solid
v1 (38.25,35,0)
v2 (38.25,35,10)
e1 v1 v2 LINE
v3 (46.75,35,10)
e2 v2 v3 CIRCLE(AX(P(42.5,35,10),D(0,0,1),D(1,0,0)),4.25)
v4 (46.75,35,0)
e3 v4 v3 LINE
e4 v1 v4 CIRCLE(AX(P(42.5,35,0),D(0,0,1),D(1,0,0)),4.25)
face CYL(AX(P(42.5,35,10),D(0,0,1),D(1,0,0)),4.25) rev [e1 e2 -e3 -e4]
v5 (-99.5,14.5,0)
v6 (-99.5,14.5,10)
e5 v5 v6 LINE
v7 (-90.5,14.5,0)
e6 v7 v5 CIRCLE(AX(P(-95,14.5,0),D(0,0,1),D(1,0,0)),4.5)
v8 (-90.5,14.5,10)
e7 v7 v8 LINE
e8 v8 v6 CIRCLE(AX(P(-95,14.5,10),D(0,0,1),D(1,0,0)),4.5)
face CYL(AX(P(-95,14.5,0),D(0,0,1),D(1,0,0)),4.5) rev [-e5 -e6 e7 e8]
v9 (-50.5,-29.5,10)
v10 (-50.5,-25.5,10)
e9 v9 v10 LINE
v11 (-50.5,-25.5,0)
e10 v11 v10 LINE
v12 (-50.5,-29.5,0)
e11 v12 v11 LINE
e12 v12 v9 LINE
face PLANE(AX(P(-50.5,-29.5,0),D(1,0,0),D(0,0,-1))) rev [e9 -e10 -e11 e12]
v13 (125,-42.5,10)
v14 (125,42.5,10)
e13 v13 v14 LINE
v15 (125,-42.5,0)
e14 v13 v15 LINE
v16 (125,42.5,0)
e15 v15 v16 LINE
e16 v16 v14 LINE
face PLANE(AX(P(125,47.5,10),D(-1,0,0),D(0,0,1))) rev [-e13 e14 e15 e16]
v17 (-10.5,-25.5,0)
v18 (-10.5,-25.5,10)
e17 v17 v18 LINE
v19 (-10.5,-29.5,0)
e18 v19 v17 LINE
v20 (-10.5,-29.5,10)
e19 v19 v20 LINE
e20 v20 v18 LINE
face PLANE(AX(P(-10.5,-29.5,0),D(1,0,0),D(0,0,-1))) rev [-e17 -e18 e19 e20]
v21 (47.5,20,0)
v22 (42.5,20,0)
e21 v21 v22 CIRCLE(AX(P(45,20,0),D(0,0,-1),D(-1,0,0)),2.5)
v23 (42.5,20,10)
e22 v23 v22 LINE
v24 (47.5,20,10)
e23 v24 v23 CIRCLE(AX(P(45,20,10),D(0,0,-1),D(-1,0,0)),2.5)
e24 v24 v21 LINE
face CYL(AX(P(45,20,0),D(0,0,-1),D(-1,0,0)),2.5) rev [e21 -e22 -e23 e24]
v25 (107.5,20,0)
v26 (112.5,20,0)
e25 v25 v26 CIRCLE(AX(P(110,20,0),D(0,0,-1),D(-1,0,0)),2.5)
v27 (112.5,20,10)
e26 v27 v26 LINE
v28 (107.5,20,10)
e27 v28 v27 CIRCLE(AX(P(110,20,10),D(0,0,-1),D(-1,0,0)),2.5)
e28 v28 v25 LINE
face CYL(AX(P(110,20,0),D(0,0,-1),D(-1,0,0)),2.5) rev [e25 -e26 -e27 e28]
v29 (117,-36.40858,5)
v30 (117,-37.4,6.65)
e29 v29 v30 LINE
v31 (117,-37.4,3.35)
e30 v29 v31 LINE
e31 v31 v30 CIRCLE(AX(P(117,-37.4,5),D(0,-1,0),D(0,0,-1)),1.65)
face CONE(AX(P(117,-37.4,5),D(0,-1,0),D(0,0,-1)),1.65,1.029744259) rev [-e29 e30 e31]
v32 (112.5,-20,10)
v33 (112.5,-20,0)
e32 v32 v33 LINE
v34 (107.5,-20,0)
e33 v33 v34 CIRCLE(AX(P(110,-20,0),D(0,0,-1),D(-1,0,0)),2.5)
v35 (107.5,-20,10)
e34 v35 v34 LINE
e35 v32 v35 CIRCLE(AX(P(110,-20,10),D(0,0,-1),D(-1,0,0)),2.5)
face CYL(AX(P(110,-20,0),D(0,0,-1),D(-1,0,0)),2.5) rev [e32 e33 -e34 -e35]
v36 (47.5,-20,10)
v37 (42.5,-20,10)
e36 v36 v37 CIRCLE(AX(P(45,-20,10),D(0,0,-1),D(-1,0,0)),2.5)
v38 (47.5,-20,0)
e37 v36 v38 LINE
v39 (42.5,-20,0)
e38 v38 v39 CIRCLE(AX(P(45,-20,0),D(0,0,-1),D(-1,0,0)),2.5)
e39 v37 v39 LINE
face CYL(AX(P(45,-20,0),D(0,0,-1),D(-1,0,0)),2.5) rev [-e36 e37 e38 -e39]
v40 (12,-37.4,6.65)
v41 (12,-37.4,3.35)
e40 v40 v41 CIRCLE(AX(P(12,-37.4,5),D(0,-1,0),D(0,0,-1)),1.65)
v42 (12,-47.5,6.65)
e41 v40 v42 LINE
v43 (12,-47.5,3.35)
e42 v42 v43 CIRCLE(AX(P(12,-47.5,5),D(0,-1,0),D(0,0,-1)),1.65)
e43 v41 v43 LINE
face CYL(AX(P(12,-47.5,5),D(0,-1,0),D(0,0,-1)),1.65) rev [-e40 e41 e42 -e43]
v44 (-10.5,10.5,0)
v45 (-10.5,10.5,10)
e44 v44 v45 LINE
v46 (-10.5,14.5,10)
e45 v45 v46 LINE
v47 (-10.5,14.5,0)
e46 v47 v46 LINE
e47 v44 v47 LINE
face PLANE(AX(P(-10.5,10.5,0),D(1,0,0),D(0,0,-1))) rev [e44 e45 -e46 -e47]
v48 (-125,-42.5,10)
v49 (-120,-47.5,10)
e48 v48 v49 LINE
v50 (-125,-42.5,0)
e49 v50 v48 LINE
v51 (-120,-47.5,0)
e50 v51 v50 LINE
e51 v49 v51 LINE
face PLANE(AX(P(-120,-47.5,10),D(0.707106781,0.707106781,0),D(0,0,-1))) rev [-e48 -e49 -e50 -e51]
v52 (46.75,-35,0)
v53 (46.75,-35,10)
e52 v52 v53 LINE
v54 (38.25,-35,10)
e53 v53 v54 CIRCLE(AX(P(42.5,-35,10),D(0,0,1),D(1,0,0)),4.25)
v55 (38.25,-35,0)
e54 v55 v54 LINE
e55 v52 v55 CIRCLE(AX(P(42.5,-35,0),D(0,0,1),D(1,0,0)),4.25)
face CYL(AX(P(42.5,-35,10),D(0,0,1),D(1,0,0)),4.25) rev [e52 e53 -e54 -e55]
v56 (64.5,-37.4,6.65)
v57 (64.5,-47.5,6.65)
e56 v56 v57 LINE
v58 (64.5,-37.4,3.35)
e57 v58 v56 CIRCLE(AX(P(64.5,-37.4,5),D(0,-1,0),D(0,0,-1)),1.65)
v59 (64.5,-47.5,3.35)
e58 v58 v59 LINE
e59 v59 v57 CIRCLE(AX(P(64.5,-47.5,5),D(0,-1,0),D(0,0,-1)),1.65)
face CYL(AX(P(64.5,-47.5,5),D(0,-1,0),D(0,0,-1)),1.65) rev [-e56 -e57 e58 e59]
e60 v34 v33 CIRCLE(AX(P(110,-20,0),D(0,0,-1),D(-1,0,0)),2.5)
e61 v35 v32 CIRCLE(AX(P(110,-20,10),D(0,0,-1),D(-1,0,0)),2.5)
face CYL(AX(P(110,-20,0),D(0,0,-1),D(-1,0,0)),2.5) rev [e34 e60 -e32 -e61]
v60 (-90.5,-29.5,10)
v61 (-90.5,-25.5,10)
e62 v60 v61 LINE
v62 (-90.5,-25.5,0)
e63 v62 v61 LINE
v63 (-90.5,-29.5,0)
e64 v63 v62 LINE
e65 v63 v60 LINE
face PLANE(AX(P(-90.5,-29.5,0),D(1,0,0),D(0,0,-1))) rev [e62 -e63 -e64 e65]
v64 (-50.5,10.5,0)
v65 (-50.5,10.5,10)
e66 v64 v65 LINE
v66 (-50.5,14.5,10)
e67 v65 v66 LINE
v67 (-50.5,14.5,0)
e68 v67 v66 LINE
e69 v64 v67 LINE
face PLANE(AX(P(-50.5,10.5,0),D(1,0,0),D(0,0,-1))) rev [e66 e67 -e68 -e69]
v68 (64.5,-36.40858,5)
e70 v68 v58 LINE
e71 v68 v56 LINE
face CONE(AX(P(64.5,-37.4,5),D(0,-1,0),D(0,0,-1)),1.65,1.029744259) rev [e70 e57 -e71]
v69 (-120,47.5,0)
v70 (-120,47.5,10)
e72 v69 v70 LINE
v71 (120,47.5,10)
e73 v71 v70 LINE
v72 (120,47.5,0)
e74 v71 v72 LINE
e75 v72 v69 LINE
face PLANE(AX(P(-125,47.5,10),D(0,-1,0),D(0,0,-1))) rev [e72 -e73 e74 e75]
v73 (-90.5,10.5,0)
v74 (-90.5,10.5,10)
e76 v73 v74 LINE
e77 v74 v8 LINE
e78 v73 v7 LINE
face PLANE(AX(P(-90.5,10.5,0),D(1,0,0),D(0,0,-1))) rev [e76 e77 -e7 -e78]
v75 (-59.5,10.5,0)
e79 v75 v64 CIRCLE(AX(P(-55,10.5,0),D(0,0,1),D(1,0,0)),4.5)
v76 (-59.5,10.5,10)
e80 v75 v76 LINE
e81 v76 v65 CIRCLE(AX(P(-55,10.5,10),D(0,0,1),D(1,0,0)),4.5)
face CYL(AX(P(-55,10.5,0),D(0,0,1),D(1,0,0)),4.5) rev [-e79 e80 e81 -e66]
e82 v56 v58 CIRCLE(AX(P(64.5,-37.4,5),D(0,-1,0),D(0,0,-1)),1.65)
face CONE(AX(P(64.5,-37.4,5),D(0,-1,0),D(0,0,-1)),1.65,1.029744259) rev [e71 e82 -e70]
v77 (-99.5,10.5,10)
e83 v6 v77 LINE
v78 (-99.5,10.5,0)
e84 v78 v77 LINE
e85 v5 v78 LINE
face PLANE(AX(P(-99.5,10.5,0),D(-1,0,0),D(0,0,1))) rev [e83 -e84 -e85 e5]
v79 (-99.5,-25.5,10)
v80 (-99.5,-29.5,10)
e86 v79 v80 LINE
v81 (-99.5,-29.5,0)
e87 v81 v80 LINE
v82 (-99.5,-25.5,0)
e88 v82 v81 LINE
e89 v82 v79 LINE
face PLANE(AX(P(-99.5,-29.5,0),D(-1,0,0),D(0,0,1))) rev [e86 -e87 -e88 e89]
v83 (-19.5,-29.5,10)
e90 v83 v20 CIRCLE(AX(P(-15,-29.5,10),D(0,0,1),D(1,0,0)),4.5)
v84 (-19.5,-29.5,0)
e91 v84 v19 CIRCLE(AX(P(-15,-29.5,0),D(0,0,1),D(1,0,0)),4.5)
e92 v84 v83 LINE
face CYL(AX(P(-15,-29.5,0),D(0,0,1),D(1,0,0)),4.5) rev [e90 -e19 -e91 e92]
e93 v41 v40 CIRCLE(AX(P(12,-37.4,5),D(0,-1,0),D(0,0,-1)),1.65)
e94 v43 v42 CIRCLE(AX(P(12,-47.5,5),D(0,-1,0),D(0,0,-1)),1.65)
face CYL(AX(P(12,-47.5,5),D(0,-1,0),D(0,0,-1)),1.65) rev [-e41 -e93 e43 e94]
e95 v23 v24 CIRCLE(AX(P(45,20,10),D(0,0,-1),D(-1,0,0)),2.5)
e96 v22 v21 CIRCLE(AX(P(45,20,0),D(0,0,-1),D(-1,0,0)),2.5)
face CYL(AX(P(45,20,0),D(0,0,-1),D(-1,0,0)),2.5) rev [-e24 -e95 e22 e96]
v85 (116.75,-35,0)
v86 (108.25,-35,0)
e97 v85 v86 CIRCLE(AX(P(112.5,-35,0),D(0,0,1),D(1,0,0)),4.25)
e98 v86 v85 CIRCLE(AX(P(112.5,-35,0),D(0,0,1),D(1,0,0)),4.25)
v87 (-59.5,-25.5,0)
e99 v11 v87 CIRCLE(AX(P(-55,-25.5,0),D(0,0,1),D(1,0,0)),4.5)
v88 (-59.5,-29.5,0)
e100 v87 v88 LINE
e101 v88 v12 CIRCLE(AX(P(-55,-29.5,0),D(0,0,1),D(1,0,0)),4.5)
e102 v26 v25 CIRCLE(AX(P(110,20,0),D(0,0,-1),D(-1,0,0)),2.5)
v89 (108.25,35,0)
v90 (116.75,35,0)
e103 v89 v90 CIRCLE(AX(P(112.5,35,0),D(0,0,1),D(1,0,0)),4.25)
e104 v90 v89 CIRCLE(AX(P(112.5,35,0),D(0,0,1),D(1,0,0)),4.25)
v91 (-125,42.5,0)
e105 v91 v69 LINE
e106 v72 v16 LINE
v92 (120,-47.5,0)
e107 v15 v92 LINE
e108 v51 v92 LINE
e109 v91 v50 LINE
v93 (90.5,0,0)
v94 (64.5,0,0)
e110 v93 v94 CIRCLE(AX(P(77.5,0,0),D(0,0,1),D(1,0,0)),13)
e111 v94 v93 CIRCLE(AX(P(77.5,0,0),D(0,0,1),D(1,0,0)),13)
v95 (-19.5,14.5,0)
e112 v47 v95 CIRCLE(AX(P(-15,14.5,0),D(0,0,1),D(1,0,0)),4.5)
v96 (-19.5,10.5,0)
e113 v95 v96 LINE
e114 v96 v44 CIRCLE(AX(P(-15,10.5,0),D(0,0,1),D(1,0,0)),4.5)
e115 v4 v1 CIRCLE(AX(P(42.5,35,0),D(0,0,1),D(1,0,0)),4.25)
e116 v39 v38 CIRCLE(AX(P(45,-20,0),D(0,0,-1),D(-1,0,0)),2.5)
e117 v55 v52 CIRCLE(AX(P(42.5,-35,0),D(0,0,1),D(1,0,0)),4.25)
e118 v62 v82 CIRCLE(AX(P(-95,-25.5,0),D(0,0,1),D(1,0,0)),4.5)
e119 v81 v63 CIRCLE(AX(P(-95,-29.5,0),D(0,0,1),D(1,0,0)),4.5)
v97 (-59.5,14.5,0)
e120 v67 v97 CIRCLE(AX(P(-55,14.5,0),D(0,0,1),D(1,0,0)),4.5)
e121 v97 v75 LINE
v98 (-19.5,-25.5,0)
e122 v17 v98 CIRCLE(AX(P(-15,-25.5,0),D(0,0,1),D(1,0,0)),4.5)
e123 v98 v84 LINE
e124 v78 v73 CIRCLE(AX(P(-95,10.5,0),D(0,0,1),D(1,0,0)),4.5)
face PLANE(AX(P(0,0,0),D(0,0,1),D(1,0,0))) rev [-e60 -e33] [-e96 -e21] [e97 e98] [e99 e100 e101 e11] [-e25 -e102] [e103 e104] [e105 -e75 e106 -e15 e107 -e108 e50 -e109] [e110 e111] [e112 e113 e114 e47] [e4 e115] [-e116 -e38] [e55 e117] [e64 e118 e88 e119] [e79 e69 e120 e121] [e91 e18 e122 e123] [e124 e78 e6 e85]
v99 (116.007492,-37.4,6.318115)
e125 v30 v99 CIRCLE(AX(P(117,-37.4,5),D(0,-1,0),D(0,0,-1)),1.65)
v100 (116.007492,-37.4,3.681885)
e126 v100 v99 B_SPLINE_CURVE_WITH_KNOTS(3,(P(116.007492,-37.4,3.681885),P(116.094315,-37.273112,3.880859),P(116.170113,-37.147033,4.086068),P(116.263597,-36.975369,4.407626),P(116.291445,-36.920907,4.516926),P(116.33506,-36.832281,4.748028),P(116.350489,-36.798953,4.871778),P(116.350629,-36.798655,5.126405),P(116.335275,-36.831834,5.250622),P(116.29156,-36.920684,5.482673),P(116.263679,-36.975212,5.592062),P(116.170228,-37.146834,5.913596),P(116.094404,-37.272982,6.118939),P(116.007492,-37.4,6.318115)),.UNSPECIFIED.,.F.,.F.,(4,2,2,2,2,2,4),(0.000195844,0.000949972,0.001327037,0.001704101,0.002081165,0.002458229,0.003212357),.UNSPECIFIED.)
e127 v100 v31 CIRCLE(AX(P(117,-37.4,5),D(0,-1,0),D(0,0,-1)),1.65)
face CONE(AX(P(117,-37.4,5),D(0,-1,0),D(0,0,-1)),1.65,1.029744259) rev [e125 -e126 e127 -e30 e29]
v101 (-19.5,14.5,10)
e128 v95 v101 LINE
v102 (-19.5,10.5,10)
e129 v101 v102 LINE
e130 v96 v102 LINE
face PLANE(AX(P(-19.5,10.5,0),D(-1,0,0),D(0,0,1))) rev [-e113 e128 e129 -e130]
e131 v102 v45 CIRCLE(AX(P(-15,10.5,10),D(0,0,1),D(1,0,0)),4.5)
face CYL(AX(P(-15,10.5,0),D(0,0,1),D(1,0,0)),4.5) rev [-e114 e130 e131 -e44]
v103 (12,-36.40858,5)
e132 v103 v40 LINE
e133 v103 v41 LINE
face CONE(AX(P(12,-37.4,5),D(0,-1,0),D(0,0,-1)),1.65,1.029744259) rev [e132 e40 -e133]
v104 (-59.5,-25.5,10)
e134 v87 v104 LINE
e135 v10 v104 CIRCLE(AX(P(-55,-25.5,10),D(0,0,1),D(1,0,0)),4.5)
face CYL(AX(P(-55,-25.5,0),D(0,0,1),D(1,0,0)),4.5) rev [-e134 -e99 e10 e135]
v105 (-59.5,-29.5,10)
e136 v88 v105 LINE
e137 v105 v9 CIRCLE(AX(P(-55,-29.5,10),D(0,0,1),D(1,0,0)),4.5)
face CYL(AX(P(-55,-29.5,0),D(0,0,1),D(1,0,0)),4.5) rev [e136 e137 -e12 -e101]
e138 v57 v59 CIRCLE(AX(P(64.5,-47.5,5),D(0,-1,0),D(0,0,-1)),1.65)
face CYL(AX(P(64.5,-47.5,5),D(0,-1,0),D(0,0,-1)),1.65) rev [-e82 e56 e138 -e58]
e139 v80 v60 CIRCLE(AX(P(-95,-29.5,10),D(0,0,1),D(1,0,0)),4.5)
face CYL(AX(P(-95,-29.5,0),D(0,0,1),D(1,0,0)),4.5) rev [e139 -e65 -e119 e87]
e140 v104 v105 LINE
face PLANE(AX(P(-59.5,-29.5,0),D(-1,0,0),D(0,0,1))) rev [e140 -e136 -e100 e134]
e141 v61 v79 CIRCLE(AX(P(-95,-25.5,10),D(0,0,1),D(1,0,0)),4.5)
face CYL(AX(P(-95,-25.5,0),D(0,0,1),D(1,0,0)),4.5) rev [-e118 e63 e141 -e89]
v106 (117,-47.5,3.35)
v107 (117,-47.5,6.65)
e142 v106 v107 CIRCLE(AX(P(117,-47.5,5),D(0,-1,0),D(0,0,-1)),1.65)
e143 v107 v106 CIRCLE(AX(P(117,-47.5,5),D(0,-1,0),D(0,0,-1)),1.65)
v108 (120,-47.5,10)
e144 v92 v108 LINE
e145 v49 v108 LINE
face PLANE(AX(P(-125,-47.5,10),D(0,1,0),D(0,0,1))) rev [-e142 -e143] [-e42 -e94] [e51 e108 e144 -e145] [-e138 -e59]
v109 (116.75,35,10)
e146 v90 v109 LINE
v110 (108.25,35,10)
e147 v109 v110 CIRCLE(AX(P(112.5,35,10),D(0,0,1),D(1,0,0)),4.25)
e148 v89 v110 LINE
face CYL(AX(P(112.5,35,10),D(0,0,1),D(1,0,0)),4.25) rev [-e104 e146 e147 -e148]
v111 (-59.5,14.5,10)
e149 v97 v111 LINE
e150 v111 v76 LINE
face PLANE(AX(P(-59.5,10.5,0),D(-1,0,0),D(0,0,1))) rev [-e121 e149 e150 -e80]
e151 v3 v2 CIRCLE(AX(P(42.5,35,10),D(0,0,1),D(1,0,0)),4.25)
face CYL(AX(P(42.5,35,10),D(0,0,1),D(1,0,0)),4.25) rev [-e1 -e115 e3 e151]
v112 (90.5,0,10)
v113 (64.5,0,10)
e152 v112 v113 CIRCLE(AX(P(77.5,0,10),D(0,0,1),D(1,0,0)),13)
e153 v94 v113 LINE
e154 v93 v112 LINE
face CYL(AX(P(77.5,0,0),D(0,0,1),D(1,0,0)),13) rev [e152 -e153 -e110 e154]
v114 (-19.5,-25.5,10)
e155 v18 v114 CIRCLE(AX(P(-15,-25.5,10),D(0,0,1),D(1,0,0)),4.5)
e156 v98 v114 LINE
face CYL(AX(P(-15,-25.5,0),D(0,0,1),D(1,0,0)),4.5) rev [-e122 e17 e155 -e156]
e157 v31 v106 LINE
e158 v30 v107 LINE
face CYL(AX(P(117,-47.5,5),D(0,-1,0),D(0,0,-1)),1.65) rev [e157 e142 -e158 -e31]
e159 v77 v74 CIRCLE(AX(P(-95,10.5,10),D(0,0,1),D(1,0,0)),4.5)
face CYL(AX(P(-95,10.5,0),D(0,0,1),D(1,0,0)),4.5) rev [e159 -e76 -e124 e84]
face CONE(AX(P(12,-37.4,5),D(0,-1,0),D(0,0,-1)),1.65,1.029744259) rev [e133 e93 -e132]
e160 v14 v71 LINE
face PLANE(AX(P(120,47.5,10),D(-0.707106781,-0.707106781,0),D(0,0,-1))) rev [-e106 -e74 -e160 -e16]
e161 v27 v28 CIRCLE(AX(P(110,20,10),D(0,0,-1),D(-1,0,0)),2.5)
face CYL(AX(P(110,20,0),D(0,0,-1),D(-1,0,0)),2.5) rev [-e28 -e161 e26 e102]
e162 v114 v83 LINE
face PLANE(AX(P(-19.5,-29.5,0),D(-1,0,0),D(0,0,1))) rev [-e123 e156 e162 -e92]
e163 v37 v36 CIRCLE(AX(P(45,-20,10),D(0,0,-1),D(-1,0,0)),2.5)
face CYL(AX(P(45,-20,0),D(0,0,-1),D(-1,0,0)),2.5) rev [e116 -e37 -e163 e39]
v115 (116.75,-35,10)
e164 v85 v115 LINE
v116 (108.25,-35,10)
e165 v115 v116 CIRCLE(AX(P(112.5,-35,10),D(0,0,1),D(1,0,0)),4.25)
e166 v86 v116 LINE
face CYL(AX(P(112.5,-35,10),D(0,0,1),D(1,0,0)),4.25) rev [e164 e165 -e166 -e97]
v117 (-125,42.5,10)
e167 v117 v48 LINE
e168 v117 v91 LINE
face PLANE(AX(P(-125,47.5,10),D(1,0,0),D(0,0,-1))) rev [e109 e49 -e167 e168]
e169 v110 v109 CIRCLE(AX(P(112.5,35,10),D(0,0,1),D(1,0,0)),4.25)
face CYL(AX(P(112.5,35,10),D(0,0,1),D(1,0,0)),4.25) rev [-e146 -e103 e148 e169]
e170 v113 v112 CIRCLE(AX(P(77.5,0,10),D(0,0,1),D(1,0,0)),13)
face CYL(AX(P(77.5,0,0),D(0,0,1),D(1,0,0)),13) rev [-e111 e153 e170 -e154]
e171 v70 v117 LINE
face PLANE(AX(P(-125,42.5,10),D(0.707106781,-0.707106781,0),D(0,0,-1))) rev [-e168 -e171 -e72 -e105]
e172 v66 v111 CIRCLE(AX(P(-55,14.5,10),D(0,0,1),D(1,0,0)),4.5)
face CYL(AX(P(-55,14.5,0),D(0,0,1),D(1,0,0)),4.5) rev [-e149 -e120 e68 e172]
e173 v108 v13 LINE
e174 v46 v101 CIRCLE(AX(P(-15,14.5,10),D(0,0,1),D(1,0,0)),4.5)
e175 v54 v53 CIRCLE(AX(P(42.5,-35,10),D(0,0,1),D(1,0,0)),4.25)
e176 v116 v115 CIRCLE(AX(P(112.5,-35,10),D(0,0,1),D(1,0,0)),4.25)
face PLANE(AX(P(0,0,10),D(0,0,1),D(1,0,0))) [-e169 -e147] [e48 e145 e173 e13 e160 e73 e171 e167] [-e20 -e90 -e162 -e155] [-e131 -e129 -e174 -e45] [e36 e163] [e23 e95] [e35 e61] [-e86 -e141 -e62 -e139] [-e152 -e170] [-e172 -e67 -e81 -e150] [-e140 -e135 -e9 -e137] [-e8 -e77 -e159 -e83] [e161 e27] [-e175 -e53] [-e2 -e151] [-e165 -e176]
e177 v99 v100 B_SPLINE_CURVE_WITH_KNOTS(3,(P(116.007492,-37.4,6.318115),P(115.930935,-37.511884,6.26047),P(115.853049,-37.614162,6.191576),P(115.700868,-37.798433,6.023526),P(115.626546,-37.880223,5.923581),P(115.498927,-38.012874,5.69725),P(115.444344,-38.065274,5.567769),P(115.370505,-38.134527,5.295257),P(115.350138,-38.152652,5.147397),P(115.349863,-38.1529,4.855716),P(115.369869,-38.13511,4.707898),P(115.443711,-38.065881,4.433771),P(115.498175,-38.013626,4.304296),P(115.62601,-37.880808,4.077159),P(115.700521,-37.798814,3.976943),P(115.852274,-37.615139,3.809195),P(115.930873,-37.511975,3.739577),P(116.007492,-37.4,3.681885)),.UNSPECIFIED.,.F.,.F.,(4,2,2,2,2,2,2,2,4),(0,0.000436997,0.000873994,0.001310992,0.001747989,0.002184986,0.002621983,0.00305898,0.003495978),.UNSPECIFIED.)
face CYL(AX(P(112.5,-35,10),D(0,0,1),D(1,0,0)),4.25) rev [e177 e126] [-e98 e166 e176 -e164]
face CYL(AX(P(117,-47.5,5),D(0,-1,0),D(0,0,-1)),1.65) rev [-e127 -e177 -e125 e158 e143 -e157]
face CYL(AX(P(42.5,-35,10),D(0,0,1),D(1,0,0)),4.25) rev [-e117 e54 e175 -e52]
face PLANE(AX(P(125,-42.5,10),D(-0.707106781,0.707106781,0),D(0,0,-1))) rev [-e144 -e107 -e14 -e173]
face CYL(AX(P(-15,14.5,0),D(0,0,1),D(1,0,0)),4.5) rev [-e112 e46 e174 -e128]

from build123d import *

# Parameters (mm, degrees)
SKETCH_1_W                  = 250
SKETCH_1_H                  = 95
EXTRUDE_1_DEPTH             = 10
CUT_EXTRUDE_2_DEPTH         = 135.094183319
PATTERN_LINEAR_1_COUNT      = 2
PATTERN_LINEAR_1_PITCH      = 40
PATTERN_LINEAR_1_COUNT_DIR2 = 2
PATTERN_LINEAR_1_PITCH_DIR2 = 40
PATTERN_LINEAR_2_COUNT      = 2
PATTERN_LINEAR_2_PITCH      = 40
PATTERN_LINEAR_2_COUNT_DIR2 = 2
PATTERN_LINEAR_2_PITCH_DIR2 = 40
CHAMFER_1_SIZE              = 5
HOLE_WIZARD_M10_3_D         = 8.5
HOLE_WIZARD_M10_3_DEPTH     = 24.5
HOLE_WIZARD_M10_3_TIP       = 2.553657631
SKETCH_12_R                 = 13
CUT_EXTRUDE_5_DEPTH         = 135.094183319
HOLE_WIZARD_M6_1_D          = 5
HOLE_WIZARD_M4_1_D          = 3.3
HOLE_WIZARD_M4_1_DEPTH      = 10.1
HOLE_WIZARD_M4_1_TIP        = 0.991420021


with BuildPart() as part:
    # 草图1 → 凸台-拉伸1 (new body)
    with BuildSketch(Plane.XY):
        Rectangle(SKETCH_1_W, SKETCH_1_H)
    extrude(amount=EXTRUDE_1_DEPTH)

    # 草图3 → 切除-拉伸2 (cut, through all)
    with BuildSketch(Plane.XY.offset(10)):
        with BuildLine():
            Line((-59.5, -29.5), (-59.5, -25.5))
            ThreePointArc((-59.5, -25.5), (-55, -21), (-50.5, -25.5))
            Line((-50.5, -25.5), (-50.5, -29.5))
            ThreePointArc((-50.5, -29.5), (-55, -34), (-59.5, -29.5))
        make_face()
    cut_extrude_2 = extrude(amount=-CUT_EXTRUDE_2_DEPTH, mode=Mode.SUBTRACT)

    # 阵列(线性)1: Cut-Extrude 2 2 × 2
    with Locations(*[(i * PATTERN_LINEAR_1_PITCH, j * PATTERN_LINEAR_1_PITCH_DIR2, 0) for i in range(PATTERN_LINEAR_1_COUNT) for j in range(PATTERN_LINEAR_1_COUNT_DIR2) if (i, j) != (0, 0)]):
        add(cut_extrude_2, mode=Mode.SUBTRACT)

    # 阵列(线性)2: Cut-Extrude 2 2 × 2
    with Locations(*[(-i * PATTERN_LINEAR_2_PITCH, j * PATTERN_LINEAR_2_PITCH_DIR2, 0) for i in range(PATTERN_LINEAR_2_COUNT) for j in range(PATTERN_LINEAR_2_COUNT_DIR2) if (i, j) != (0, 0)]):
        add(cut_extrude_2, mode=Mode.SUBTRACT)

    # 倒角1
    chamfer_1_edges = [part.edges().sort_by_distance(p)[0] for p in [
        (125, -47.5, 5),
        (-125, -47.5, 5),
        (-125, 47.5, 5),
        (125, 47.5, 5),
    ]]
    chamfer(chamfer_1_edges, length=CHAMFER_1_SIZE)

    # M10 螺纹孔3
    with Locations(Plane(origin=(42.5, 35, 10), x_dir=(1, 0, 0), z_dir=(0, 0, 1))):
        with Locations((0, 0), (70, 0), (70, -70), (0, -70)):
            Hole(HOLE_WIZARD_M10_3_D / 2, depth=HOLE_WIZARD_M10_3_DEPTH)
            with Locations((0, 0, -(HOLE_WIZARD_M10_3_DEPTH + HOLE_WIZARD_M10_3_TIP / 2))):  # 118° drill point
                Cone(0, HOLE_WIZARD_M10_3_D / 2, HOLE_WIZARD_M10_3_TIP, mode=Mode.SUBTRACT)

    # 草图12 → 切除-拉伸5 (cut, through all)
    with BuildSketch(Plane.XY.offset(10)):
        with Locations((77.5, 0)):
            Circle(SKETCH_12_R)
    extrude(amount=-CUT_EXTRUDE_5_DEPTH, mode=Mode.SUBTRACT)

    # M6 螺纹孔1 (through all)
    with Locations(Plane(origin=(45, -20, 0), x_dir=(-1, 0, 0), z_dir=(0, 0, -1))):
        with Locations((0, 0), (-65, 0), (-65, 40), (0, 40)):
            Hole(HOLE_WIZARD_M6_1_D / 2)

    # M4 螺纹孔1
    with Locations(Plane(origin=(117, -47.5, 5), x_dir=(0, 0, -1), z_dir=(0, -1, 0))):
        with Locations((0, 0), (0, -105), (0, -52.5)):
            Hole(HOLE_WIZARD_M4_1_D / 2, depth=HOLE_WIZARD_M4_1_DEPTH)
            with Locations((0, 0, -(HOLE_WIZARD_M4_1_DEPTH + HOLE_WIZARD_M4_1_TIP / 2))):  # 118° drill point
                Cone(0, HOLE_WIZARD_M4_1_D / 2, HOLE_WIZARD_M4_1_TIP, mode=Mode.SUBTRACT)


solid = part.part
